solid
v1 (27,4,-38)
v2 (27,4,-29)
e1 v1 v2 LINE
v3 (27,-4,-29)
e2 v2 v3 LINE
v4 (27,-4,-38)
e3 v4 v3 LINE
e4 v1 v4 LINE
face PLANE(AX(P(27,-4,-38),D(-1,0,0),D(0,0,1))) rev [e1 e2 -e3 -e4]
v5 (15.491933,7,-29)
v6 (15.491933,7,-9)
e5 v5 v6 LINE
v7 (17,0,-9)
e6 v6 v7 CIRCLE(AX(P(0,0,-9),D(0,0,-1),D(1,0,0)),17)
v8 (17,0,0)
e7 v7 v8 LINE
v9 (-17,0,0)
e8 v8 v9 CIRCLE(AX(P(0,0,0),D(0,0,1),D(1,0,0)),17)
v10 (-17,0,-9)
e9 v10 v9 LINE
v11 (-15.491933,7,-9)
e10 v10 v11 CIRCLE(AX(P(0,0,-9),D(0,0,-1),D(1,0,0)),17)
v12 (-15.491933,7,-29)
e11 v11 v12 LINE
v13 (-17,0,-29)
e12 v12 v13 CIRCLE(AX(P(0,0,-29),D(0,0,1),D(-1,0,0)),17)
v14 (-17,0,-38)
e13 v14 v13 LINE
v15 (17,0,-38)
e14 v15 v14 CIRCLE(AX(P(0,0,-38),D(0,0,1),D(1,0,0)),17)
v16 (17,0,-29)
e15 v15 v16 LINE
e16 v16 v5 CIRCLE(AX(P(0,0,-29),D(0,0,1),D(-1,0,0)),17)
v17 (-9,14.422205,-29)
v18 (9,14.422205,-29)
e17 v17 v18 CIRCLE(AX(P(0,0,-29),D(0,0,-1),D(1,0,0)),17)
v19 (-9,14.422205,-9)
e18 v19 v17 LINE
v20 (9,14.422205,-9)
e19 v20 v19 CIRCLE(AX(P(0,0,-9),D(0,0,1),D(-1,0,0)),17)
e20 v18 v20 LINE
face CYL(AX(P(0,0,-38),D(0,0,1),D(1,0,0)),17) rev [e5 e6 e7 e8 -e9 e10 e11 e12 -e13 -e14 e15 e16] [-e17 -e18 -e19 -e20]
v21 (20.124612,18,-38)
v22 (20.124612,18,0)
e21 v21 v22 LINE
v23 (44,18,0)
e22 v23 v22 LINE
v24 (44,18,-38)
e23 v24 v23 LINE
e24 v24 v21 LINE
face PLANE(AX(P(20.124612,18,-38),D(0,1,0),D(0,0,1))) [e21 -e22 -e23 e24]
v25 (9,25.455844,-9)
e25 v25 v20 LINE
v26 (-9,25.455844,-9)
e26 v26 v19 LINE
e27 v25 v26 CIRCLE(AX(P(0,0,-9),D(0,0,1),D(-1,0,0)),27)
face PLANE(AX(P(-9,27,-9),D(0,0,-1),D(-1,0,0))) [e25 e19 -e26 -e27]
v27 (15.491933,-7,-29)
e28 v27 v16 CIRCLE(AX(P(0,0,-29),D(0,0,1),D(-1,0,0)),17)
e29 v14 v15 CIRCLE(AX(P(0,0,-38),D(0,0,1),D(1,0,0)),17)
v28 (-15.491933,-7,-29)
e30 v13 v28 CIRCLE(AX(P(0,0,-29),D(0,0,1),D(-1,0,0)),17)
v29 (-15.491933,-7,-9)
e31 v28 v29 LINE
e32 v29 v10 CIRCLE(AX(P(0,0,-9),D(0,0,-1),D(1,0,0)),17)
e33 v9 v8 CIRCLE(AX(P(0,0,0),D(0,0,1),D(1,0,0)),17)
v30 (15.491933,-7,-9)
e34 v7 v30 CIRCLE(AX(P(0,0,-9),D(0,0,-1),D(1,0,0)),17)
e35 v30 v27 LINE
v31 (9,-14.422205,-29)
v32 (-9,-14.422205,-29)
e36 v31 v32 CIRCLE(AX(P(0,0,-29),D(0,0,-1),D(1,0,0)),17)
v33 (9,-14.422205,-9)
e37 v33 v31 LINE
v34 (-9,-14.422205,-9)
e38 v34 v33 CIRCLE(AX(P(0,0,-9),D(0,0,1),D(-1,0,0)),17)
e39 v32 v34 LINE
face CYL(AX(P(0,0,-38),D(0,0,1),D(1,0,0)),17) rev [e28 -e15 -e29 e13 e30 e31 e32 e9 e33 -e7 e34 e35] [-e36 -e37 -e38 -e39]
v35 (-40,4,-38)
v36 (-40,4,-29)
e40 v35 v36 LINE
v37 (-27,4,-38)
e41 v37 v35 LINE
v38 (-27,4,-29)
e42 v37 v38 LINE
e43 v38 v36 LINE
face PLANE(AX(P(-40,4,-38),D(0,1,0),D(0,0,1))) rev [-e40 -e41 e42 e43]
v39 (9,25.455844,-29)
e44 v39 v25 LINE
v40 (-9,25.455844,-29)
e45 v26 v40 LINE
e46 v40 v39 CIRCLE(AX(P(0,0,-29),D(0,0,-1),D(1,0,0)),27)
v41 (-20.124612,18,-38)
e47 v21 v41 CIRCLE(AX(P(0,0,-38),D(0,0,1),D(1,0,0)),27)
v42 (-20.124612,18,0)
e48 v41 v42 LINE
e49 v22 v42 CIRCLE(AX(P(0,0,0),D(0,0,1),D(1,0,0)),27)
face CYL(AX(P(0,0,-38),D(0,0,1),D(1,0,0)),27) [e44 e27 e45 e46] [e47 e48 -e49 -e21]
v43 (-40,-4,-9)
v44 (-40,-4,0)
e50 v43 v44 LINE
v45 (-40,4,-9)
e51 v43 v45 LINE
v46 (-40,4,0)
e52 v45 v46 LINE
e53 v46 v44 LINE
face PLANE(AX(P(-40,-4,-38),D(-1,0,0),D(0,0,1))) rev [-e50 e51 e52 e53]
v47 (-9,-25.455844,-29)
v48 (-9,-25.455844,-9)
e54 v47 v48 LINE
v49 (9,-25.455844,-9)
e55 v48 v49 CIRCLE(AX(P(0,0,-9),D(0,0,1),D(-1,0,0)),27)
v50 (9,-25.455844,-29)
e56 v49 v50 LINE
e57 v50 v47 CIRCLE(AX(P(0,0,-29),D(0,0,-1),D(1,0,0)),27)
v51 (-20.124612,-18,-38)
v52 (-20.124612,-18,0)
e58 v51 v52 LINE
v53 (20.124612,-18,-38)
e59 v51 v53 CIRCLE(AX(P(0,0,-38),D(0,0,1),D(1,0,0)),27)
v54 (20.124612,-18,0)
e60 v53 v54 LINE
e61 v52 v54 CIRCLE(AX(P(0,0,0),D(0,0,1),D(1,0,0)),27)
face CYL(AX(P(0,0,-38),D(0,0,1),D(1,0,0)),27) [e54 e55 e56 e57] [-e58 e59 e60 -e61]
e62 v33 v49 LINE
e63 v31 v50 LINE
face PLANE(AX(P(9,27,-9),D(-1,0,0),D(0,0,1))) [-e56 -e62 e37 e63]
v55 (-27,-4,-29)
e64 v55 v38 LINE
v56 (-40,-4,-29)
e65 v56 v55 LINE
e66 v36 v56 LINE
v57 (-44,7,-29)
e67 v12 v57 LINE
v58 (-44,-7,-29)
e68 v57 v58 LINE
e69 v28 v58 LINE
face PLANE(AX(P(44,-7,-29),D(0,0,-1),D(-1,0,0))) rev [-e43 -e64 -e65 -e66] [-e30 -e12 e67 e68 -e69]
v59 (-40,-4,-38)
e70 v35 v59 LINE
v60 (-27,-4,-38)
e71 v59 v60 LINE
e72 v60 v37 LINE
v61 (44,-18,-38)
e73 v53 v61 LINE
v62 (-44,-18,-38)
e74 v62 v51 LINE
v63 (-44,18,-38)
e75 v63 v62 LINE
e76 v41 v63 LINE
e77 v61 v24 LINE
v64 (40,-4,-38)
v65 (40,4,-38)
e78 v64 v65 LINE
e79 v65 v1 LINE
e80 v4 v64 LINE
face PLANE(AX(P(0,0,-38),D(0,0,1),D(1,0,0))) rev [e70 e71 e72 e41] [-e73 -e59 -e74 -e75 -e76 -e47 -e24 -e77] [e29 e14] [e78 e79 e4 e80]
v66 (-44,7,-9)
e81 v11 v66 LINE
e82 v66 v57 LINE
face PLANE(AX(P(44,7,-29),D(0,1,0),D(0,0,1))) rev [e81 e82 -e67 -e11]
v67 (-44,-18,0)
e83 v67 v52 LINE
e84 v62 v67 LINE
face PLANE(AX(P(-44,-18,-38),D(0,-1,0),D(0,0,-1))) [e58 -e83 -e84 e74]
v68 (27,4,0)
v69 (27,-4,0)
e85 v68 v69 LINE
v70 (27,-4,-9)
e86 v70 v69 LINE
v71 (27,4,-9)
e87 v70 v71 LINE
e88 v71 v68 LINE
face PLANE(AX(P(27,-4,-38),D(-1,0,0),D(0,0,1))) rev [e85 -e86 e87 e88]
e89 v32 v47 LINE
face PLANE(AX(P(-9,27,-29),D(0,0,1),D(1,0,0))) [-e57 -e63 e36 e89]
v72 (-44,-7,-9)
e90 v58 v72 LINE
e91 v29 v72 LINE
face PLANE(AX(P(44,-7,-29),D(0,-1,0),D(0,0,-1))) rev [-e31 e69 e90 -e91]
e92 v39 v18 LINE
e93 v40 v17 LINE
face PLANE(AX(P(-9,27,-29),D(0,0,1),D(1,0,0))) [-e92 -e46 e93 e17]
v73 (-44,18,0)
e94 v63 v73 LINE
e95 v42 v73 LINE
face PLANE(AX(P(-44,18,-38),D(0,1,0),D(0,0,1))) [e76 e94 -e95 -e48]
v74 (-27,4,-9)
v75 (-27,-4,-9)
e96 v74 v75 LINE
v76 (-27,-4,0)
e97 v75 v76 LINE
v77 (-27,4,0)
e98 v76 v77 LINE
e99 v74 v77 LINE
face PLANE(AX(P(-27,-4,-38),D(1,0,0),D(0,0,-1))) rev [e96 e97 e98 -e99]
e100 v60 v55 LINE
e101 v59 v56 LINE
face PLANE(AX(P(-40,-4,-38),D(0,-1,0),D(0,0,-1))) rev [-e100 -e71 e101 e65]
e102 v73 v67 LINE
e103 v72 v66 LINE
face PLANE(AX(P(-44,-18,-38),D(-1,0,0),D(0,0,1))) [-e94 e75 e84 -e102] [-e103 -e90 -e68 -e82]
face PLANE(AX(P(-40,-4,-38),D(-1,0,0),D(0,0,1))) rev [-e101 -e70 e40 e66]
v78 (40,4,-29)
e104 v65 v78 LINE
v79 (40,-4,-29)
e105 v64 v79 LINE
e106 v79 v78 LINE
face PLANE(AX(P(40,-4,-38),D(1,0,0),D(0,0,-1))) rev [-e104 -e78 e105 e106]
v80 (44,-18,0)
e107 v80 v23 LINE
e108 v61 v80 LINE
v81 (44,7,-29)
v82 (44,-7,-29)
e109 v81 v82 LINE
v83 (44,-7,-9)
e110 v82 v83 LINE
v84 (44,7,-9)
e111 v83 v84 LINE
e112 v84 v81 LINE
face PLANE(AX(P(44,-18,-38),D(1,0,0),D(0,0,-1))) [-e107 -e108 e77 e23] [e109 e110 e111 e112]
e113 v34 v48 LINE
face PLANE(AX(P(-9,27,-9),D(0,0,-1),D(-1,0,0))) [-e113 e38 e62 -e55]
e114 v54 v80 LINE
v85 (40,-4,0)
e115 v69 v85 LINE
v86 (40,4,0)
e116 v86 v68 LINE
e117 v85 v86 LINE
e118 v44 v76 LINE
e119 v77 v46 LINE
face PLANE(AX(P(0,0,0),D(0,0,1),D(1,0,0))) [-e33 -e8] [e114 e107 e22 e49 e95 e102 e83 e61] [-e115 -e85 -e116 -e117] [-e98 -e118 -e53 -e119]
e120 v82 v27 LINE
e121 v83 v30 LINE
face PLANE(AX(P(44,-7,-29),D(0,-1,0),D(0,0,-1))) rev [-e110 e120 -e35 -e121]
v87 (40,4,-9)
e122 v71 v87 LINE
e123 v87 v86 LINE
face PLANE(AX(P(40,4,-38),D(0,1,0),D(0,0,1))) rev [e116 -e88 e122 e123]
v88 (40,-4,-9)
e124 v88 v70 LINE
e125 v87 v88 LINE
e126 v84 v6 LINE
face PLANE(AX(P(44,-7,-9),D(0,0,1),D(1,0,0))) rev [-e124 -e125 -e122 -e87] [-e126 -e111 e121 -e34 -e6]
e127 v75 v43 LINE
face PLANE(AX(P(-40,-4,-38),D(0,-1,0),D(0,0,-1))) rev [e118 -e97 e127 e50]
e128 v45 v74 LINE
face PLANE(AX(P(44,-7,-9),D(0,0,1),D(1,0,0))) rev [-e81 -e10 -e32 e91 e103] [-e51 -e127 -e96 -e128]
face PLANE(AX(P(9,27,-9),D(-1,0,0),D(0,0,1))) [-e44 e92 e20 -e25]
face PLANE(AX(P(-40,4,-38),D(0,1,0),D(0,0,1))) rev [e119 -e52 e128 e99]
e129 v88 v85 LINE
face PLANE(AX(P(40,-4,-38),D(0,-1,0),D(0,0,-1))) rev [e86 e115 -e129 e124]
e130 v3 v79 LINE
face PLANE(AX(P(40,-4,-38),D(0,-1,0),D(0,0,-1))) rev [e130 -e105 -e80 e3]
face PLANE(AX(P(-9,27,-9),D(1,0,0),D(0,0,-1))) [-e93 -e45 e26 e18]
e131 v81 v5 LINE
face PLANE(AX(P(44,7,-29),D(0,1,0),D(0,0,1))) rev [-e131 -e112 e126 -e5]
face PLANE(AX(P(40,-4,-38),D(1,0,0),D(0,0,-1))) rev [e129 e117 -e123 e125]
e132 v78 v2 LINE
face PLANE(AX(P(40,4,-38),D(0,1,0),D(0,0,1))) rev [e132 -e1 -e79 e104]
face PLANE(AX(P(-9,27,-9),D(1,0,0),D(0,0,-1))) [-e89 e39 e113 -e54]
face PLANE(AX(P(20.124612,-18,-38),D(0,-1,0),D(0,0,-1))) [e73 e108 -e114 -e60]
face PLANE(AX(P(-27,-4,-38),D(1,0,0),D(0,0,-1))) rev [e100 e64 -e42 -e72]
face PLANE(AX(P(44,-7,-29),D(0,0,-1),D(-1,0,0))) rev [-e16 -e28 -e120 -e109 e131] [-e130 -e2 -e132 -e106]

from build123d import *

# Parameters (mm, degrees)
BODY_PROFILE_SKETCH_R       = 17
BODY_PROFILE_SKETCH_W       = 13
BODY_PROFILE_SKETCH_H       = 8
BODY_EXTRUDE_38MM_DEPTH     = 38
WINDOW_CUT_20X14_DEPTH      = 100.584135283
WINDOW_CUT_20X14_DEPTH_BACK = 100.584135283
WINDOW_20X14_SKETCH_W       = 20
WINDOW_20X14_SKETCH_H       = 14
WINDOW_CUT_18X20_DEPTH      = 74.518705103
WINDOW_CUT_18X20_DEPTH_BACK = 74.518705103
WINDOW_18X20_SKETCH_W       = 18
WINDOW_18X20_SKETCH_H       = 20


with BuildPart() as part:
    # Body Profile Sketch → Body Extrude 38mm (new body)
    with BuildSketch(Plane.XY):
        with BuildLine():
            Line((-44, -18), (-20.124611797, -18))
            ThreePointArc((-20.124611797, -18), (0, -27), (20.124611797, -18))
            Line((20.124611797, -18), (44, -18))
            Line((44, -18), (44, 18))
            Line((44, 18), (20.124611797, 18))
            ThreePointArc((20.124611797, 18), (0, 27), (-20.124611797, 18))
            Line((-20.124611797, 18), (-44, 18))
            Line((-44, 18), (-44, -18))
        make_face()
        Circle(BODY_PROFILE_SKETCH_R, mode=Mode.SUBTRACT)
        with Locations((-33.5, 0)):
            Rectangle(BODY_PROFILE_SKETCH_W, BODY_PROFILE_SKETCH_H, mode=Mode.SUBTRACT)
        with Locations((33.5, 0)):
            Rectangle(BODY_PROFILE_SKETCH_W, BODY_PROFILE_SKETCH_H, mode=Mode.SUBTRACT)
    extrude(amount=-BODY_EXTRUDE_38MM_DEPTH)

    # Window 20x14 Sketch → Window Cut 20x14 (cut, two sides: drawn at the far end of the back side and taken through both)
    with BuildSketch(Plane.ZY.offset(44).offset(-WINDOW_CUT_20X14_DEPTH_BACK)):
        with Locations((-19, 0)):
            Rectangle(WINDOW_20X14_SKETCH_W, WINDOW_20X14_SKETCH_H)
    extrude(amount=WINDOW_CUT_20X14_DEPTH + WINDOW_CUT_20X14_DEPTH_BACK, mode=Mode.SUBTRACT)

    # Window 18x20 Sketch → Window Cut 18x20 (cut, two sides: drawn at the far end of the back side and taken through both)
    with BuildSketch(Plane(origin=(0, 18, 0), x_dir=(1, 0, 0), z_dir=(0, 1, 0)).offset(-WINDOW_CUT_18X20_DEPTH_BACK)):
        with Locations((0, 19)):
            Rectangle(WINDOW_18X20_SKETCH_W, WINDOW_18X20_SKETCH_H)
    extrude(amount=WINDOW_CUT_18X20_DEPTH + WINDOW_CUT_18X20_DEPTH_BACK, mode=Mode.SUBTRACT)


solid = part.part
